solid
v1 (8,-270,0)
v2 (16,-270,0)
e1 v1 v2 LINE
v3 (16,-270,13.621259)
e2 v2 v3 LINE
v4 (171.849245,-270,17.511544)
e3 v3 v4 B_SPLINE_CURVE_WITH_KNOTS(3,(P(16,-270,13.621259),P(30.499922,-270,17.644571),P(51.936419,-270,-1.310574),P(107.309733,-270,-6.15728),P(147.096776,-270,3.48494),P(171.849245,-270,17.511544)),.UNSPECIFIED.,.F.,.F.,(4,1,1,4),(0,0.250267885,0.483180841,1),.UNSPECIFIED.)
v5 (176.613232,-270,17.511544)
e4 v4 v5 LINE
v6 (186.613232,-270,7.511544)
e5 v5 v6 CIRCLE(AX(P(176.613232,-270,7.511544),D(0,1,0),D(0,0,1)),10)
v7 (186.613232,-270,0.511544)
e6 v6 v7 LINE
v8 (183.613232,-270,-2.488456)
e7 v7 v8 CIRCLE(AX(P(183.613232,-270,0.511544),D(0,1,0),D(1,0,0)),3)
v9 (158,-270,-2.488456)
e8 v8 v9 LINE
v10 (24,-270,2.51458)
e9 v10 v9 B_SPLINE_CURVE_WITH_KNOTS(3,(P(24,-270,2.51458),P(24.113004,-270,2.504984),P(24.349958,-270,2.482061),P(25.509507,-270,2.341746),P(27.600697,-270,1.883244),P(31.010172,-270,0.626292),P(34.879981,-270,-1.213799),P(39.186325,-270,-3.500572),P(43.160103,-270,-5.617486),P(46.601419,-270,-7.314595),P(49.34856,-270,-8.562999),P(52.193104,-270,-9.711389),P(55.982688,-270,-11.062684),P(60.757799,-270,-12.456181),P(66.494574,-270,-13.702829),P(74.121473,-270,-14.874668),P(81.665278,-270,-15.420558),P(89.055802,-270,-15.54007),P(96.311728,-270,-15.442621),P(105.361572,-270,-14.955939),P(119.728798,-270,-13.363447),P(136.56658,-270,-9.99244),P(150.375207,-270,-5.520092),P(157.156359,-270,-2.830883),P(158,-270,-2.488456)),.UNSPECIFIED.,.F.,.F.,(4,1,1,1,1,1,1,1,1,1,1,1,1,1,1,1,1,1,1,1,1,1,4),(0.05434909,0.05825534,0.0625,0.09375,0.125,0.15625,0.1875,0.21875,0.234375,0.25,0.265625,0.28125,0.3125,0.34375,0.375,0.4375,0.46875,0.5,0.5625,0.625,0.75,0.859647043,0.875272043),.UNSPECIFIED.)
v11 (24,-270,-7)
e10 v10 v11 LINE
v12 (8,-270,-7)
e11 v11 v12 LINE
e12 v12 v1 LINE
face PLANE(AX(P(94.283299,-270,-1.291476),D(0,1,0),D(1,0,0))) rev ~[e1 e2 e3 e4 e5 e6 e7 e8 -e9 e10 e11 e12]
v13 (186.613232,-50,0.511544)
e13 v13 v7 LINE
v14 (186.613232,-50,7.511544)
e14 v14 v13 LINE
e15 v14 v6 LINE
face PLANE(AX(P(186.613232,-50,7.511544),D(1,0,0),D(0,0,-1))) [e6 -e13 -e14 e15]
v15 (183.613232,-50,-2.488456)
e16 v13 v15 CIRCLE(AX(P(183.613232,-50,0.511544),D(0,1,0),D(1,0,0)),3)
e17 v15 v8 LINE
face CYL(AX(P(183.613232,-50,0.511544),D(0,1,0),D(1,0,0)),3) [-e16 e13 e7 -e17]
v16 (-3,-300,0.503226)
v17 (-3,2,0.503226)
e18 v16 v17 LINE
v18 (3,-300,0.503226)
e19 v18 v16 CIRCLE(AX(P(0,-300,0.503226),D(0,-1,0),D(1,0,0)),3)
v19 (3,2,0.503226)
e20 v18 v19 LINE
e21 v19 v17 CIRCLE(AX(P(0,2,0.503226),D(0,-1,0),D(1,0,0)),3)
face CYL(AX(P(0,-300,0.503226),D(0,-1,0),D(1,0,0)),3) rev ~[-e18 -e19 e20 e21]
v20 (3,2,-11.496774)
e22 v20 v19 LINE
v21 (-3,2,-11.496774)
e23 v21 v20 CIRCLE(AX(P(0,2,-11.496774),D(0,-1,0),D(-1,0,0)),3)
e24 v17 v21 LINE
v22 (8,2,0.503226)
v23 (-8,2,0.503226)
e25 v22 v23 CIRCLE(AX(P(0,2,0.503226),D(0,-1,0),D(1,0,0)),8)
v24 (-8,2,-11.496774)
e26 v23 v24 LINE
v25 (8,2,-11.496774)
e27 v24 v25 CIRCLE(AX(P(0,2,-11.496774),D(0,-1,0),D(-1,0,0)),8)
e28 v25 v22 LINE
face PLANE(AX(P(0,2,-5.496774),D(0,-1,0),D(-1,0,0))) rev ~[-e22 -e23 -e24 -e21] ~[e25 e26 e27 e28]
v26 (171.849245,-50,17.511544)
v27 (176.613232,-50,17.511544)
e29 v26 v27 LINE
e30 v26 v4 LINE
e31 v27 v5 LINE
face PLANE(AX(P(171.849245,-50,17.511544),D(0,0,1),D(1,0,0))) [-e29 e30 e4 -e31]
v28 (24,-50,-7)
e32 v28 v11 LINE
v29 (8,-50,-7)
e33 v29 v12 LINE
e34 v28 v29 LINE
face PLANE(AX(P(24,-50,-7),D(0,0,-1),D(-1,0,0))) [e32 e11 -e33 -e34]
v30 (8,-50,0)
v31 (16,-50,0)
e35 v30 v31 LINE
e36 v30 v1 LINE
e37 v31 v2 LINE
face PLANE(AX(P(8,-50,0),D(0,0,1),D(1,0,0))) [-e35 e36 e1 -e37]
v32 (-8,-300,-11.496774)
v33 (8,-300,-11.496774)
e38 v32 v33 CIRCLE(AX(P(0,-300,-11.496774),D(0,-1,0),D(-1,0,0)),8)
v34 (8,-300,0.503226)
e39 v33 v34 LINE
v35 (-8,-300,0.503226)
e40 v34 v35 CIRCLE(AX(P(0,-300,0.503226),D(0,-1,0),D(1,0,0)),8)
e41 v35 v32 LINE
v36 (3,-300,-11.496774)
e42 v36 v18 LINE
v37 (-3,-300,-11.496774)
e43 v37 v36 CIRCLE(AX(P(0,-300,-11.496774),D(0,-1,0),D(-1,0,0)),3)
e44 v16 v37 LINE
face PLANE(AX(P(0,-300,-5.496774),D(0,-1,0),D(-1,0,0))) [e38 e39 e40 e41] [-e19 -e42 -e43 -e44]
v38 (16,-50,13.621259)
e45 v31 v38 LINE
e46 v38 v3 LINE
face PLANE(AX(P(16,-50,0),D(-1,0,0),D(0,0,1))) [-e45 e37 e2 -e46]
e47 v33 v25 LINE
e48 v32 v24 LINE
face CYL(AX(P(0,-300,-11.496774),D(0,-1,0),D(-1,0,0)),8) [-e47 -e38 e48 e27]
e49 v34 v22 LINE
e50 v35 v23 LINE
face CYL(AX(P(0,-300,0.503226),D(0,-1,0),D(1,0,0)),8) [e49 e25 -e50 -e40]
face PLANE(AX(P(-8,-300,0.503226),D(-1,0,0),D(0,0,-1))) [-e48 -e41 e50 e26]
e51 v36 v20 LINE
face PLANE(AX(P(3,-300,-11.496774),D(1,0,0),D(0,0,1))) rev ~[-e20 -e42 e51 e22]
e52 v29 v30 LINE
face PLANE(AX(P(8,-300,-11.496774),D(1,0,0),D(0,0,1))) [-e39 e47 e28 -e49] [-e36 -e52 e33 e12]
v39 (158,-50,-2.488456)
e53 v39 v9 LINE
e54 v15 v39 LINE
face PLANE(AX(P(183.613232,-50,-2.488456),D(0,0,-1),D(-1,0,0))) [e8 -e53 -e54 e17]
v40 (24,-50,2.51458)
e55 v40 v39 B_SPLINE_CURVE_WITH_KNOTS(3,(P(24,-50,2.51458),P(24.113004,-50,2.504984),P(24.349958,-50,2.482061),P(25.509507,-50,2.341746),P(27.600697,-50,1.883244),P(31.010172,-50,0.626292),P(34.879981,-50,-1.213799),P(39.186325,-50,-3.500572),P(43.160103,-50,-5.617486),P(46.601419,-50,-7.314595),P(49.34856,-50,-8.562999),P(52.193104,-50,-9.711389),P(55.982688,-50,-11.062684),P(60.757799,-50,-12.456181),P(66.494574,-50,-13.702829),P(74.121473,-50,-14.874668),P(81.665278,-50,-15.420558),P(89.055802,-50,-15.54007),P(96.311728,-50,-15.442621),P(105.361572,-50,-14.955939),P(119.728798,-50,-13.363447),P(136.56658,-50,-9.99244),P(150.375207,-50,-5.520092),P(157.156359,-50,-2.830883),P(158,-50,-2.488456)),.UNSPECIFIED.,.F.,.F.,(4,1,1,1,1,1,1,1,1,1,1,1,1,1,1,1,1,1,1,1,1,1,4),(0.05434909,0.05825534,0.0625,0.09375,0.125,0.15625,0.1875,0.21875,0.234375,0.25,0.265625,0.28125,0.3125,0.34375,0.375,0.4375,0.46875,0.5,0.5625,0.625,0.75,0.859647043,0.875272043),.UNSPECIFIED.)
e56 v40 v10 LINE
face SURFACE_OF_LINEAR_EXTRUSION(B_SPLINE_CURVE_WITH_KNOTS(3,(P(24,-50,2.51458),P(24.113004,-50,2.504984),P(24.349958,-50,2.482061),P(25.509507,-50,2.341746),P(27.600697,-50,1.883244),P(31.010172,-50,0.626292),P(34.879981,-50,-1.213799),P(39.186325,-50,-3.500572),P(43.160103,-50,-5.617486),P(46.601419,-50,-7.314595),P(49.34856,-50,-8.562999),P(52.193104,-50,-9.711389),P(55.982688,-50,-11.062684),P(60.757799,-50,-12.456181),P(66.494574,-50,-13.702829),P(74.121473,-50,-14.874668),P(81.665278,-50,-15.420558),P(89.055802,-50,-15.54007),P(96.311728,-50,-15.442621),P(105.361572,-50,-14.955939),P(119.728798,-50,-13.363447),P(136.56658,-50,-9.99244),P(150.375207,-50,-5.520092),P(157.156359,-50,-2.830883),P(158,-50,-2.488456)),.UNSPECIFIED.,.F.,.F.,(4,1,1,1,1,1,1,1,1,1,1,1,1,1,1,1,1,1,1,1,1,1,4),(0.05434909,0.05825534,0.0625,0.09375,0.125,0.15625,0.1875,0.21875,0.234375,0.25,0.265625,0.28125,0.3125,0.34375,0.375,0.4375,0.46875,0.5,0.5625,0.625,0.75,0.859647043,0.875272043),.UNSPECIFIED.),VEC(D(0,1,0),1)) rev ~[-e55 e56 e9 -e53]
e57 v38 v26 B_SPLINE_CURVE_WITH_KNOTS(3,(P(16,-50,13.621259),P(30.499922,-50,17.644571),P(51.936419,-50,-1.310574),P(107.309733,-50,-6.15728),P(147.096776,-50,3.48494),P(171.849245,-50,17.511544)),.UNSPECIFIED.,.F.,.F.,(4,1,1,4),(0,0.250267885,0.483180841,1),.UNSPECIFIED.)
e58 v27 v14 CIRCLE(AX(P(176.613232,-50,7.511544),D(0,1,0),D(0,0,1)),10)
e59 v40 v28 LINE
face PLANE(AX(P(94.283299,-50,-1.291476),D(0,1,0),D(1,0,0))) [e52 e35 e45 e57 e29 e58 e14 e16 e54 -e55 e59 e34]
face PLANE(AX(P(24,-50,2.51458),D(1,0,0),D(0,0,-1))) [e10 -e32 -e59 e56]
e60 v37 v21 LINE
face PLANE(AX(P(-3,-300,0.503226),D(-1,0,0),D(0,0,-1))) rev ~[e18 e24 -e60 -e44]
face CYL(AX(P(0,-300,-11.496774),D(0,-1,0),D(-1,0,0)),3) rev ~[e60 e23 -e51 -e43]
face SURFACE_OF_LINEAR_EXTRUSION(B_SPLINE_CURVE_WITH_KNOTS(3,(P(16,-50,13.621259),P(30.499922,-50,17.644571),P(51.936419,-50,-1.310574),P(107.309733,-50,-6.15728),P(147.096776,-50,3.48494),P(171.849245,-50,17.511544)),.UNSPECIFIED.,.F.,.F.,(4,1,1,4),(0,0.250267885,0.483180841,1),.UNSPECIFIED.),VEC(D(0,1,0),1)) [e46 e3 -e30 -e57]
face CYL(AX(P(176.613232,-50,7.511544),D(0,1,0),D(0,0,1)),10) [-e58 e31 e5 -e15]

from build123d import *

# Parameters (mm, degrees)
EXTRUDE_THIN1_DEPTH      = 2
EXTRUDE_THIN1_DEPTH_BACK = 300
BOSS_EXTRUDE1_START      = -50
BOSS_EXTRUDE1_DEPTH      = 220


with BuildPart() as part:
    # Sketch1 → Extrude-Thin1 (new, two sides: drawn at the far end of the back side and taken through both)
    with BuildSketch(Plane(origin=(0, 0, 0), x_dir=(1, 0, 0), z_dir=(0, 1, 0)).offset(-EXTRUDE_THIN1_DEPTH_BACK)):
        with BuildLine():
            Line((-8, -0.503225806), (-8, 11.496774194))
            ThreePointArc((-8, 11.496774194), (0, 19.496774194), (8, 11.496774194))
            Line((8, 11.496774194), (8, -0.503225806))
            ThreePointArc((8, -0.503225806), (0, -8.503225806), (-8, -0.503225806))
        make_face()
        with BuildLine():
            Line((-3, -0.503225806), (-3, 11.496774194))
            ThreePointArc((-3, 11.496774194), (0, 14.496774194), (3, 11.496774194))
            Line((3, 11.496774194), (3, -0.503225806))
            ThreePointArc((3, -0.503225806), (0, -3.503225806), (-3, -0.503225806))
        make_face(mode=Mode.SUBTRACT)
    extrude(amount=EXTRUDE_THIN1_DEPTH + EXTRUDE_THIN1_DEPTH_BACK)

    # Sketch3 → Boss-Extrude1 (add)
    with BuildSketch(Plane(origin=(0, 0, 0), x_dir=(1, 0, 0), z_dir=(0, 1, 0)).offset(BOSS_EXTRUDE1_START)):
        with BuildLine():
            Line((8, 0), (16, 0))
            Line((16, 0), (16, -13.621259212))
            add(Edge.make_bspline(
                [(16, -13.621259212), (30.499922351, -17.644570766), (51.936419213, 1.310573607), (107.30973254, 6.157280303), (147.096775614, -3.484939683), (171.849245201, -17.511543594)],
                knots=[0, 0, 0, 0, 0.250267885, 0.483180841, 1, 1, 1, 1], degree=3))
            Line((171.849245201, -17.511543594), (176.613232431, -17.511543594))
            ThreePointArc((176.613232431, -17.511543594), (183.684300243, -14.582611406), (186.613232431, -7.511543594))
            Line((186.613232431, -7.511543594), (186.613232431, -0.511543594))
            ThreePointArc((186.613232431, -0.511543594), (185.734552774, 1.60977675), (183.613232431, 2.488456406))
            Line((183.613232431, 2.488456406), (158, 2.488456406))
            add(Edge.make_bspline(
                [(24, -2.514580028), (24.113004411, -2.504983511), (24.349957742, -2.482060724), (25.509506663, -2.341745989), (27.600697432, -1.88324406), (31.010172468, -0.626291734), (34.87998125, 1.213798693), (39.186324623, 3.500572248), (43.160103091, 5.617485681), (46.601418923, 7.314594934), (49.348560323, 8.562999499), (52.193103542, 9.711388614), (55.982687982, 11.062684309), (60.757798847, 12.456180642), (66.494574497, 13.702828567), (74.121472863, 14.874668238), (81.665278055, 15.420557925), (89.055802359, 15.540070459), (96.311727988, 15.442620679), (105.361571511, 14.955938635), (119.728798439, 13.363447087), (136.566579979, 9.992440329), (150.375206962, 5.520091676), (157.156359053, 2.830882837), (158, 2.488456406)],
                knots=[0.05434909, 0.05434909, 0.05434909, 0.05434909, 0.05825534, 0.0625, 0.09375, 0.125, 0.15625, 0.1875, 0.21875, 0.234375, 0.25, 0.265625, 0.28125, 0.3125, 0.34375, 0.375, 0.4375, 0.46875, 0.5, 0.5625, 0.625, 0.75, 0.859647043, 0.875272043, 0.875272043, 0.875272043, 0.875272043], degree=3))
            Line((24, -2.514580028), (24, 7))
            Line((24, 7), (8, 7))
            Line((8, 7), (8, 0))
        make_face()
    extrude(amount=-BOSS_EXTRUDE1_DEPTH)


solid = part.part
